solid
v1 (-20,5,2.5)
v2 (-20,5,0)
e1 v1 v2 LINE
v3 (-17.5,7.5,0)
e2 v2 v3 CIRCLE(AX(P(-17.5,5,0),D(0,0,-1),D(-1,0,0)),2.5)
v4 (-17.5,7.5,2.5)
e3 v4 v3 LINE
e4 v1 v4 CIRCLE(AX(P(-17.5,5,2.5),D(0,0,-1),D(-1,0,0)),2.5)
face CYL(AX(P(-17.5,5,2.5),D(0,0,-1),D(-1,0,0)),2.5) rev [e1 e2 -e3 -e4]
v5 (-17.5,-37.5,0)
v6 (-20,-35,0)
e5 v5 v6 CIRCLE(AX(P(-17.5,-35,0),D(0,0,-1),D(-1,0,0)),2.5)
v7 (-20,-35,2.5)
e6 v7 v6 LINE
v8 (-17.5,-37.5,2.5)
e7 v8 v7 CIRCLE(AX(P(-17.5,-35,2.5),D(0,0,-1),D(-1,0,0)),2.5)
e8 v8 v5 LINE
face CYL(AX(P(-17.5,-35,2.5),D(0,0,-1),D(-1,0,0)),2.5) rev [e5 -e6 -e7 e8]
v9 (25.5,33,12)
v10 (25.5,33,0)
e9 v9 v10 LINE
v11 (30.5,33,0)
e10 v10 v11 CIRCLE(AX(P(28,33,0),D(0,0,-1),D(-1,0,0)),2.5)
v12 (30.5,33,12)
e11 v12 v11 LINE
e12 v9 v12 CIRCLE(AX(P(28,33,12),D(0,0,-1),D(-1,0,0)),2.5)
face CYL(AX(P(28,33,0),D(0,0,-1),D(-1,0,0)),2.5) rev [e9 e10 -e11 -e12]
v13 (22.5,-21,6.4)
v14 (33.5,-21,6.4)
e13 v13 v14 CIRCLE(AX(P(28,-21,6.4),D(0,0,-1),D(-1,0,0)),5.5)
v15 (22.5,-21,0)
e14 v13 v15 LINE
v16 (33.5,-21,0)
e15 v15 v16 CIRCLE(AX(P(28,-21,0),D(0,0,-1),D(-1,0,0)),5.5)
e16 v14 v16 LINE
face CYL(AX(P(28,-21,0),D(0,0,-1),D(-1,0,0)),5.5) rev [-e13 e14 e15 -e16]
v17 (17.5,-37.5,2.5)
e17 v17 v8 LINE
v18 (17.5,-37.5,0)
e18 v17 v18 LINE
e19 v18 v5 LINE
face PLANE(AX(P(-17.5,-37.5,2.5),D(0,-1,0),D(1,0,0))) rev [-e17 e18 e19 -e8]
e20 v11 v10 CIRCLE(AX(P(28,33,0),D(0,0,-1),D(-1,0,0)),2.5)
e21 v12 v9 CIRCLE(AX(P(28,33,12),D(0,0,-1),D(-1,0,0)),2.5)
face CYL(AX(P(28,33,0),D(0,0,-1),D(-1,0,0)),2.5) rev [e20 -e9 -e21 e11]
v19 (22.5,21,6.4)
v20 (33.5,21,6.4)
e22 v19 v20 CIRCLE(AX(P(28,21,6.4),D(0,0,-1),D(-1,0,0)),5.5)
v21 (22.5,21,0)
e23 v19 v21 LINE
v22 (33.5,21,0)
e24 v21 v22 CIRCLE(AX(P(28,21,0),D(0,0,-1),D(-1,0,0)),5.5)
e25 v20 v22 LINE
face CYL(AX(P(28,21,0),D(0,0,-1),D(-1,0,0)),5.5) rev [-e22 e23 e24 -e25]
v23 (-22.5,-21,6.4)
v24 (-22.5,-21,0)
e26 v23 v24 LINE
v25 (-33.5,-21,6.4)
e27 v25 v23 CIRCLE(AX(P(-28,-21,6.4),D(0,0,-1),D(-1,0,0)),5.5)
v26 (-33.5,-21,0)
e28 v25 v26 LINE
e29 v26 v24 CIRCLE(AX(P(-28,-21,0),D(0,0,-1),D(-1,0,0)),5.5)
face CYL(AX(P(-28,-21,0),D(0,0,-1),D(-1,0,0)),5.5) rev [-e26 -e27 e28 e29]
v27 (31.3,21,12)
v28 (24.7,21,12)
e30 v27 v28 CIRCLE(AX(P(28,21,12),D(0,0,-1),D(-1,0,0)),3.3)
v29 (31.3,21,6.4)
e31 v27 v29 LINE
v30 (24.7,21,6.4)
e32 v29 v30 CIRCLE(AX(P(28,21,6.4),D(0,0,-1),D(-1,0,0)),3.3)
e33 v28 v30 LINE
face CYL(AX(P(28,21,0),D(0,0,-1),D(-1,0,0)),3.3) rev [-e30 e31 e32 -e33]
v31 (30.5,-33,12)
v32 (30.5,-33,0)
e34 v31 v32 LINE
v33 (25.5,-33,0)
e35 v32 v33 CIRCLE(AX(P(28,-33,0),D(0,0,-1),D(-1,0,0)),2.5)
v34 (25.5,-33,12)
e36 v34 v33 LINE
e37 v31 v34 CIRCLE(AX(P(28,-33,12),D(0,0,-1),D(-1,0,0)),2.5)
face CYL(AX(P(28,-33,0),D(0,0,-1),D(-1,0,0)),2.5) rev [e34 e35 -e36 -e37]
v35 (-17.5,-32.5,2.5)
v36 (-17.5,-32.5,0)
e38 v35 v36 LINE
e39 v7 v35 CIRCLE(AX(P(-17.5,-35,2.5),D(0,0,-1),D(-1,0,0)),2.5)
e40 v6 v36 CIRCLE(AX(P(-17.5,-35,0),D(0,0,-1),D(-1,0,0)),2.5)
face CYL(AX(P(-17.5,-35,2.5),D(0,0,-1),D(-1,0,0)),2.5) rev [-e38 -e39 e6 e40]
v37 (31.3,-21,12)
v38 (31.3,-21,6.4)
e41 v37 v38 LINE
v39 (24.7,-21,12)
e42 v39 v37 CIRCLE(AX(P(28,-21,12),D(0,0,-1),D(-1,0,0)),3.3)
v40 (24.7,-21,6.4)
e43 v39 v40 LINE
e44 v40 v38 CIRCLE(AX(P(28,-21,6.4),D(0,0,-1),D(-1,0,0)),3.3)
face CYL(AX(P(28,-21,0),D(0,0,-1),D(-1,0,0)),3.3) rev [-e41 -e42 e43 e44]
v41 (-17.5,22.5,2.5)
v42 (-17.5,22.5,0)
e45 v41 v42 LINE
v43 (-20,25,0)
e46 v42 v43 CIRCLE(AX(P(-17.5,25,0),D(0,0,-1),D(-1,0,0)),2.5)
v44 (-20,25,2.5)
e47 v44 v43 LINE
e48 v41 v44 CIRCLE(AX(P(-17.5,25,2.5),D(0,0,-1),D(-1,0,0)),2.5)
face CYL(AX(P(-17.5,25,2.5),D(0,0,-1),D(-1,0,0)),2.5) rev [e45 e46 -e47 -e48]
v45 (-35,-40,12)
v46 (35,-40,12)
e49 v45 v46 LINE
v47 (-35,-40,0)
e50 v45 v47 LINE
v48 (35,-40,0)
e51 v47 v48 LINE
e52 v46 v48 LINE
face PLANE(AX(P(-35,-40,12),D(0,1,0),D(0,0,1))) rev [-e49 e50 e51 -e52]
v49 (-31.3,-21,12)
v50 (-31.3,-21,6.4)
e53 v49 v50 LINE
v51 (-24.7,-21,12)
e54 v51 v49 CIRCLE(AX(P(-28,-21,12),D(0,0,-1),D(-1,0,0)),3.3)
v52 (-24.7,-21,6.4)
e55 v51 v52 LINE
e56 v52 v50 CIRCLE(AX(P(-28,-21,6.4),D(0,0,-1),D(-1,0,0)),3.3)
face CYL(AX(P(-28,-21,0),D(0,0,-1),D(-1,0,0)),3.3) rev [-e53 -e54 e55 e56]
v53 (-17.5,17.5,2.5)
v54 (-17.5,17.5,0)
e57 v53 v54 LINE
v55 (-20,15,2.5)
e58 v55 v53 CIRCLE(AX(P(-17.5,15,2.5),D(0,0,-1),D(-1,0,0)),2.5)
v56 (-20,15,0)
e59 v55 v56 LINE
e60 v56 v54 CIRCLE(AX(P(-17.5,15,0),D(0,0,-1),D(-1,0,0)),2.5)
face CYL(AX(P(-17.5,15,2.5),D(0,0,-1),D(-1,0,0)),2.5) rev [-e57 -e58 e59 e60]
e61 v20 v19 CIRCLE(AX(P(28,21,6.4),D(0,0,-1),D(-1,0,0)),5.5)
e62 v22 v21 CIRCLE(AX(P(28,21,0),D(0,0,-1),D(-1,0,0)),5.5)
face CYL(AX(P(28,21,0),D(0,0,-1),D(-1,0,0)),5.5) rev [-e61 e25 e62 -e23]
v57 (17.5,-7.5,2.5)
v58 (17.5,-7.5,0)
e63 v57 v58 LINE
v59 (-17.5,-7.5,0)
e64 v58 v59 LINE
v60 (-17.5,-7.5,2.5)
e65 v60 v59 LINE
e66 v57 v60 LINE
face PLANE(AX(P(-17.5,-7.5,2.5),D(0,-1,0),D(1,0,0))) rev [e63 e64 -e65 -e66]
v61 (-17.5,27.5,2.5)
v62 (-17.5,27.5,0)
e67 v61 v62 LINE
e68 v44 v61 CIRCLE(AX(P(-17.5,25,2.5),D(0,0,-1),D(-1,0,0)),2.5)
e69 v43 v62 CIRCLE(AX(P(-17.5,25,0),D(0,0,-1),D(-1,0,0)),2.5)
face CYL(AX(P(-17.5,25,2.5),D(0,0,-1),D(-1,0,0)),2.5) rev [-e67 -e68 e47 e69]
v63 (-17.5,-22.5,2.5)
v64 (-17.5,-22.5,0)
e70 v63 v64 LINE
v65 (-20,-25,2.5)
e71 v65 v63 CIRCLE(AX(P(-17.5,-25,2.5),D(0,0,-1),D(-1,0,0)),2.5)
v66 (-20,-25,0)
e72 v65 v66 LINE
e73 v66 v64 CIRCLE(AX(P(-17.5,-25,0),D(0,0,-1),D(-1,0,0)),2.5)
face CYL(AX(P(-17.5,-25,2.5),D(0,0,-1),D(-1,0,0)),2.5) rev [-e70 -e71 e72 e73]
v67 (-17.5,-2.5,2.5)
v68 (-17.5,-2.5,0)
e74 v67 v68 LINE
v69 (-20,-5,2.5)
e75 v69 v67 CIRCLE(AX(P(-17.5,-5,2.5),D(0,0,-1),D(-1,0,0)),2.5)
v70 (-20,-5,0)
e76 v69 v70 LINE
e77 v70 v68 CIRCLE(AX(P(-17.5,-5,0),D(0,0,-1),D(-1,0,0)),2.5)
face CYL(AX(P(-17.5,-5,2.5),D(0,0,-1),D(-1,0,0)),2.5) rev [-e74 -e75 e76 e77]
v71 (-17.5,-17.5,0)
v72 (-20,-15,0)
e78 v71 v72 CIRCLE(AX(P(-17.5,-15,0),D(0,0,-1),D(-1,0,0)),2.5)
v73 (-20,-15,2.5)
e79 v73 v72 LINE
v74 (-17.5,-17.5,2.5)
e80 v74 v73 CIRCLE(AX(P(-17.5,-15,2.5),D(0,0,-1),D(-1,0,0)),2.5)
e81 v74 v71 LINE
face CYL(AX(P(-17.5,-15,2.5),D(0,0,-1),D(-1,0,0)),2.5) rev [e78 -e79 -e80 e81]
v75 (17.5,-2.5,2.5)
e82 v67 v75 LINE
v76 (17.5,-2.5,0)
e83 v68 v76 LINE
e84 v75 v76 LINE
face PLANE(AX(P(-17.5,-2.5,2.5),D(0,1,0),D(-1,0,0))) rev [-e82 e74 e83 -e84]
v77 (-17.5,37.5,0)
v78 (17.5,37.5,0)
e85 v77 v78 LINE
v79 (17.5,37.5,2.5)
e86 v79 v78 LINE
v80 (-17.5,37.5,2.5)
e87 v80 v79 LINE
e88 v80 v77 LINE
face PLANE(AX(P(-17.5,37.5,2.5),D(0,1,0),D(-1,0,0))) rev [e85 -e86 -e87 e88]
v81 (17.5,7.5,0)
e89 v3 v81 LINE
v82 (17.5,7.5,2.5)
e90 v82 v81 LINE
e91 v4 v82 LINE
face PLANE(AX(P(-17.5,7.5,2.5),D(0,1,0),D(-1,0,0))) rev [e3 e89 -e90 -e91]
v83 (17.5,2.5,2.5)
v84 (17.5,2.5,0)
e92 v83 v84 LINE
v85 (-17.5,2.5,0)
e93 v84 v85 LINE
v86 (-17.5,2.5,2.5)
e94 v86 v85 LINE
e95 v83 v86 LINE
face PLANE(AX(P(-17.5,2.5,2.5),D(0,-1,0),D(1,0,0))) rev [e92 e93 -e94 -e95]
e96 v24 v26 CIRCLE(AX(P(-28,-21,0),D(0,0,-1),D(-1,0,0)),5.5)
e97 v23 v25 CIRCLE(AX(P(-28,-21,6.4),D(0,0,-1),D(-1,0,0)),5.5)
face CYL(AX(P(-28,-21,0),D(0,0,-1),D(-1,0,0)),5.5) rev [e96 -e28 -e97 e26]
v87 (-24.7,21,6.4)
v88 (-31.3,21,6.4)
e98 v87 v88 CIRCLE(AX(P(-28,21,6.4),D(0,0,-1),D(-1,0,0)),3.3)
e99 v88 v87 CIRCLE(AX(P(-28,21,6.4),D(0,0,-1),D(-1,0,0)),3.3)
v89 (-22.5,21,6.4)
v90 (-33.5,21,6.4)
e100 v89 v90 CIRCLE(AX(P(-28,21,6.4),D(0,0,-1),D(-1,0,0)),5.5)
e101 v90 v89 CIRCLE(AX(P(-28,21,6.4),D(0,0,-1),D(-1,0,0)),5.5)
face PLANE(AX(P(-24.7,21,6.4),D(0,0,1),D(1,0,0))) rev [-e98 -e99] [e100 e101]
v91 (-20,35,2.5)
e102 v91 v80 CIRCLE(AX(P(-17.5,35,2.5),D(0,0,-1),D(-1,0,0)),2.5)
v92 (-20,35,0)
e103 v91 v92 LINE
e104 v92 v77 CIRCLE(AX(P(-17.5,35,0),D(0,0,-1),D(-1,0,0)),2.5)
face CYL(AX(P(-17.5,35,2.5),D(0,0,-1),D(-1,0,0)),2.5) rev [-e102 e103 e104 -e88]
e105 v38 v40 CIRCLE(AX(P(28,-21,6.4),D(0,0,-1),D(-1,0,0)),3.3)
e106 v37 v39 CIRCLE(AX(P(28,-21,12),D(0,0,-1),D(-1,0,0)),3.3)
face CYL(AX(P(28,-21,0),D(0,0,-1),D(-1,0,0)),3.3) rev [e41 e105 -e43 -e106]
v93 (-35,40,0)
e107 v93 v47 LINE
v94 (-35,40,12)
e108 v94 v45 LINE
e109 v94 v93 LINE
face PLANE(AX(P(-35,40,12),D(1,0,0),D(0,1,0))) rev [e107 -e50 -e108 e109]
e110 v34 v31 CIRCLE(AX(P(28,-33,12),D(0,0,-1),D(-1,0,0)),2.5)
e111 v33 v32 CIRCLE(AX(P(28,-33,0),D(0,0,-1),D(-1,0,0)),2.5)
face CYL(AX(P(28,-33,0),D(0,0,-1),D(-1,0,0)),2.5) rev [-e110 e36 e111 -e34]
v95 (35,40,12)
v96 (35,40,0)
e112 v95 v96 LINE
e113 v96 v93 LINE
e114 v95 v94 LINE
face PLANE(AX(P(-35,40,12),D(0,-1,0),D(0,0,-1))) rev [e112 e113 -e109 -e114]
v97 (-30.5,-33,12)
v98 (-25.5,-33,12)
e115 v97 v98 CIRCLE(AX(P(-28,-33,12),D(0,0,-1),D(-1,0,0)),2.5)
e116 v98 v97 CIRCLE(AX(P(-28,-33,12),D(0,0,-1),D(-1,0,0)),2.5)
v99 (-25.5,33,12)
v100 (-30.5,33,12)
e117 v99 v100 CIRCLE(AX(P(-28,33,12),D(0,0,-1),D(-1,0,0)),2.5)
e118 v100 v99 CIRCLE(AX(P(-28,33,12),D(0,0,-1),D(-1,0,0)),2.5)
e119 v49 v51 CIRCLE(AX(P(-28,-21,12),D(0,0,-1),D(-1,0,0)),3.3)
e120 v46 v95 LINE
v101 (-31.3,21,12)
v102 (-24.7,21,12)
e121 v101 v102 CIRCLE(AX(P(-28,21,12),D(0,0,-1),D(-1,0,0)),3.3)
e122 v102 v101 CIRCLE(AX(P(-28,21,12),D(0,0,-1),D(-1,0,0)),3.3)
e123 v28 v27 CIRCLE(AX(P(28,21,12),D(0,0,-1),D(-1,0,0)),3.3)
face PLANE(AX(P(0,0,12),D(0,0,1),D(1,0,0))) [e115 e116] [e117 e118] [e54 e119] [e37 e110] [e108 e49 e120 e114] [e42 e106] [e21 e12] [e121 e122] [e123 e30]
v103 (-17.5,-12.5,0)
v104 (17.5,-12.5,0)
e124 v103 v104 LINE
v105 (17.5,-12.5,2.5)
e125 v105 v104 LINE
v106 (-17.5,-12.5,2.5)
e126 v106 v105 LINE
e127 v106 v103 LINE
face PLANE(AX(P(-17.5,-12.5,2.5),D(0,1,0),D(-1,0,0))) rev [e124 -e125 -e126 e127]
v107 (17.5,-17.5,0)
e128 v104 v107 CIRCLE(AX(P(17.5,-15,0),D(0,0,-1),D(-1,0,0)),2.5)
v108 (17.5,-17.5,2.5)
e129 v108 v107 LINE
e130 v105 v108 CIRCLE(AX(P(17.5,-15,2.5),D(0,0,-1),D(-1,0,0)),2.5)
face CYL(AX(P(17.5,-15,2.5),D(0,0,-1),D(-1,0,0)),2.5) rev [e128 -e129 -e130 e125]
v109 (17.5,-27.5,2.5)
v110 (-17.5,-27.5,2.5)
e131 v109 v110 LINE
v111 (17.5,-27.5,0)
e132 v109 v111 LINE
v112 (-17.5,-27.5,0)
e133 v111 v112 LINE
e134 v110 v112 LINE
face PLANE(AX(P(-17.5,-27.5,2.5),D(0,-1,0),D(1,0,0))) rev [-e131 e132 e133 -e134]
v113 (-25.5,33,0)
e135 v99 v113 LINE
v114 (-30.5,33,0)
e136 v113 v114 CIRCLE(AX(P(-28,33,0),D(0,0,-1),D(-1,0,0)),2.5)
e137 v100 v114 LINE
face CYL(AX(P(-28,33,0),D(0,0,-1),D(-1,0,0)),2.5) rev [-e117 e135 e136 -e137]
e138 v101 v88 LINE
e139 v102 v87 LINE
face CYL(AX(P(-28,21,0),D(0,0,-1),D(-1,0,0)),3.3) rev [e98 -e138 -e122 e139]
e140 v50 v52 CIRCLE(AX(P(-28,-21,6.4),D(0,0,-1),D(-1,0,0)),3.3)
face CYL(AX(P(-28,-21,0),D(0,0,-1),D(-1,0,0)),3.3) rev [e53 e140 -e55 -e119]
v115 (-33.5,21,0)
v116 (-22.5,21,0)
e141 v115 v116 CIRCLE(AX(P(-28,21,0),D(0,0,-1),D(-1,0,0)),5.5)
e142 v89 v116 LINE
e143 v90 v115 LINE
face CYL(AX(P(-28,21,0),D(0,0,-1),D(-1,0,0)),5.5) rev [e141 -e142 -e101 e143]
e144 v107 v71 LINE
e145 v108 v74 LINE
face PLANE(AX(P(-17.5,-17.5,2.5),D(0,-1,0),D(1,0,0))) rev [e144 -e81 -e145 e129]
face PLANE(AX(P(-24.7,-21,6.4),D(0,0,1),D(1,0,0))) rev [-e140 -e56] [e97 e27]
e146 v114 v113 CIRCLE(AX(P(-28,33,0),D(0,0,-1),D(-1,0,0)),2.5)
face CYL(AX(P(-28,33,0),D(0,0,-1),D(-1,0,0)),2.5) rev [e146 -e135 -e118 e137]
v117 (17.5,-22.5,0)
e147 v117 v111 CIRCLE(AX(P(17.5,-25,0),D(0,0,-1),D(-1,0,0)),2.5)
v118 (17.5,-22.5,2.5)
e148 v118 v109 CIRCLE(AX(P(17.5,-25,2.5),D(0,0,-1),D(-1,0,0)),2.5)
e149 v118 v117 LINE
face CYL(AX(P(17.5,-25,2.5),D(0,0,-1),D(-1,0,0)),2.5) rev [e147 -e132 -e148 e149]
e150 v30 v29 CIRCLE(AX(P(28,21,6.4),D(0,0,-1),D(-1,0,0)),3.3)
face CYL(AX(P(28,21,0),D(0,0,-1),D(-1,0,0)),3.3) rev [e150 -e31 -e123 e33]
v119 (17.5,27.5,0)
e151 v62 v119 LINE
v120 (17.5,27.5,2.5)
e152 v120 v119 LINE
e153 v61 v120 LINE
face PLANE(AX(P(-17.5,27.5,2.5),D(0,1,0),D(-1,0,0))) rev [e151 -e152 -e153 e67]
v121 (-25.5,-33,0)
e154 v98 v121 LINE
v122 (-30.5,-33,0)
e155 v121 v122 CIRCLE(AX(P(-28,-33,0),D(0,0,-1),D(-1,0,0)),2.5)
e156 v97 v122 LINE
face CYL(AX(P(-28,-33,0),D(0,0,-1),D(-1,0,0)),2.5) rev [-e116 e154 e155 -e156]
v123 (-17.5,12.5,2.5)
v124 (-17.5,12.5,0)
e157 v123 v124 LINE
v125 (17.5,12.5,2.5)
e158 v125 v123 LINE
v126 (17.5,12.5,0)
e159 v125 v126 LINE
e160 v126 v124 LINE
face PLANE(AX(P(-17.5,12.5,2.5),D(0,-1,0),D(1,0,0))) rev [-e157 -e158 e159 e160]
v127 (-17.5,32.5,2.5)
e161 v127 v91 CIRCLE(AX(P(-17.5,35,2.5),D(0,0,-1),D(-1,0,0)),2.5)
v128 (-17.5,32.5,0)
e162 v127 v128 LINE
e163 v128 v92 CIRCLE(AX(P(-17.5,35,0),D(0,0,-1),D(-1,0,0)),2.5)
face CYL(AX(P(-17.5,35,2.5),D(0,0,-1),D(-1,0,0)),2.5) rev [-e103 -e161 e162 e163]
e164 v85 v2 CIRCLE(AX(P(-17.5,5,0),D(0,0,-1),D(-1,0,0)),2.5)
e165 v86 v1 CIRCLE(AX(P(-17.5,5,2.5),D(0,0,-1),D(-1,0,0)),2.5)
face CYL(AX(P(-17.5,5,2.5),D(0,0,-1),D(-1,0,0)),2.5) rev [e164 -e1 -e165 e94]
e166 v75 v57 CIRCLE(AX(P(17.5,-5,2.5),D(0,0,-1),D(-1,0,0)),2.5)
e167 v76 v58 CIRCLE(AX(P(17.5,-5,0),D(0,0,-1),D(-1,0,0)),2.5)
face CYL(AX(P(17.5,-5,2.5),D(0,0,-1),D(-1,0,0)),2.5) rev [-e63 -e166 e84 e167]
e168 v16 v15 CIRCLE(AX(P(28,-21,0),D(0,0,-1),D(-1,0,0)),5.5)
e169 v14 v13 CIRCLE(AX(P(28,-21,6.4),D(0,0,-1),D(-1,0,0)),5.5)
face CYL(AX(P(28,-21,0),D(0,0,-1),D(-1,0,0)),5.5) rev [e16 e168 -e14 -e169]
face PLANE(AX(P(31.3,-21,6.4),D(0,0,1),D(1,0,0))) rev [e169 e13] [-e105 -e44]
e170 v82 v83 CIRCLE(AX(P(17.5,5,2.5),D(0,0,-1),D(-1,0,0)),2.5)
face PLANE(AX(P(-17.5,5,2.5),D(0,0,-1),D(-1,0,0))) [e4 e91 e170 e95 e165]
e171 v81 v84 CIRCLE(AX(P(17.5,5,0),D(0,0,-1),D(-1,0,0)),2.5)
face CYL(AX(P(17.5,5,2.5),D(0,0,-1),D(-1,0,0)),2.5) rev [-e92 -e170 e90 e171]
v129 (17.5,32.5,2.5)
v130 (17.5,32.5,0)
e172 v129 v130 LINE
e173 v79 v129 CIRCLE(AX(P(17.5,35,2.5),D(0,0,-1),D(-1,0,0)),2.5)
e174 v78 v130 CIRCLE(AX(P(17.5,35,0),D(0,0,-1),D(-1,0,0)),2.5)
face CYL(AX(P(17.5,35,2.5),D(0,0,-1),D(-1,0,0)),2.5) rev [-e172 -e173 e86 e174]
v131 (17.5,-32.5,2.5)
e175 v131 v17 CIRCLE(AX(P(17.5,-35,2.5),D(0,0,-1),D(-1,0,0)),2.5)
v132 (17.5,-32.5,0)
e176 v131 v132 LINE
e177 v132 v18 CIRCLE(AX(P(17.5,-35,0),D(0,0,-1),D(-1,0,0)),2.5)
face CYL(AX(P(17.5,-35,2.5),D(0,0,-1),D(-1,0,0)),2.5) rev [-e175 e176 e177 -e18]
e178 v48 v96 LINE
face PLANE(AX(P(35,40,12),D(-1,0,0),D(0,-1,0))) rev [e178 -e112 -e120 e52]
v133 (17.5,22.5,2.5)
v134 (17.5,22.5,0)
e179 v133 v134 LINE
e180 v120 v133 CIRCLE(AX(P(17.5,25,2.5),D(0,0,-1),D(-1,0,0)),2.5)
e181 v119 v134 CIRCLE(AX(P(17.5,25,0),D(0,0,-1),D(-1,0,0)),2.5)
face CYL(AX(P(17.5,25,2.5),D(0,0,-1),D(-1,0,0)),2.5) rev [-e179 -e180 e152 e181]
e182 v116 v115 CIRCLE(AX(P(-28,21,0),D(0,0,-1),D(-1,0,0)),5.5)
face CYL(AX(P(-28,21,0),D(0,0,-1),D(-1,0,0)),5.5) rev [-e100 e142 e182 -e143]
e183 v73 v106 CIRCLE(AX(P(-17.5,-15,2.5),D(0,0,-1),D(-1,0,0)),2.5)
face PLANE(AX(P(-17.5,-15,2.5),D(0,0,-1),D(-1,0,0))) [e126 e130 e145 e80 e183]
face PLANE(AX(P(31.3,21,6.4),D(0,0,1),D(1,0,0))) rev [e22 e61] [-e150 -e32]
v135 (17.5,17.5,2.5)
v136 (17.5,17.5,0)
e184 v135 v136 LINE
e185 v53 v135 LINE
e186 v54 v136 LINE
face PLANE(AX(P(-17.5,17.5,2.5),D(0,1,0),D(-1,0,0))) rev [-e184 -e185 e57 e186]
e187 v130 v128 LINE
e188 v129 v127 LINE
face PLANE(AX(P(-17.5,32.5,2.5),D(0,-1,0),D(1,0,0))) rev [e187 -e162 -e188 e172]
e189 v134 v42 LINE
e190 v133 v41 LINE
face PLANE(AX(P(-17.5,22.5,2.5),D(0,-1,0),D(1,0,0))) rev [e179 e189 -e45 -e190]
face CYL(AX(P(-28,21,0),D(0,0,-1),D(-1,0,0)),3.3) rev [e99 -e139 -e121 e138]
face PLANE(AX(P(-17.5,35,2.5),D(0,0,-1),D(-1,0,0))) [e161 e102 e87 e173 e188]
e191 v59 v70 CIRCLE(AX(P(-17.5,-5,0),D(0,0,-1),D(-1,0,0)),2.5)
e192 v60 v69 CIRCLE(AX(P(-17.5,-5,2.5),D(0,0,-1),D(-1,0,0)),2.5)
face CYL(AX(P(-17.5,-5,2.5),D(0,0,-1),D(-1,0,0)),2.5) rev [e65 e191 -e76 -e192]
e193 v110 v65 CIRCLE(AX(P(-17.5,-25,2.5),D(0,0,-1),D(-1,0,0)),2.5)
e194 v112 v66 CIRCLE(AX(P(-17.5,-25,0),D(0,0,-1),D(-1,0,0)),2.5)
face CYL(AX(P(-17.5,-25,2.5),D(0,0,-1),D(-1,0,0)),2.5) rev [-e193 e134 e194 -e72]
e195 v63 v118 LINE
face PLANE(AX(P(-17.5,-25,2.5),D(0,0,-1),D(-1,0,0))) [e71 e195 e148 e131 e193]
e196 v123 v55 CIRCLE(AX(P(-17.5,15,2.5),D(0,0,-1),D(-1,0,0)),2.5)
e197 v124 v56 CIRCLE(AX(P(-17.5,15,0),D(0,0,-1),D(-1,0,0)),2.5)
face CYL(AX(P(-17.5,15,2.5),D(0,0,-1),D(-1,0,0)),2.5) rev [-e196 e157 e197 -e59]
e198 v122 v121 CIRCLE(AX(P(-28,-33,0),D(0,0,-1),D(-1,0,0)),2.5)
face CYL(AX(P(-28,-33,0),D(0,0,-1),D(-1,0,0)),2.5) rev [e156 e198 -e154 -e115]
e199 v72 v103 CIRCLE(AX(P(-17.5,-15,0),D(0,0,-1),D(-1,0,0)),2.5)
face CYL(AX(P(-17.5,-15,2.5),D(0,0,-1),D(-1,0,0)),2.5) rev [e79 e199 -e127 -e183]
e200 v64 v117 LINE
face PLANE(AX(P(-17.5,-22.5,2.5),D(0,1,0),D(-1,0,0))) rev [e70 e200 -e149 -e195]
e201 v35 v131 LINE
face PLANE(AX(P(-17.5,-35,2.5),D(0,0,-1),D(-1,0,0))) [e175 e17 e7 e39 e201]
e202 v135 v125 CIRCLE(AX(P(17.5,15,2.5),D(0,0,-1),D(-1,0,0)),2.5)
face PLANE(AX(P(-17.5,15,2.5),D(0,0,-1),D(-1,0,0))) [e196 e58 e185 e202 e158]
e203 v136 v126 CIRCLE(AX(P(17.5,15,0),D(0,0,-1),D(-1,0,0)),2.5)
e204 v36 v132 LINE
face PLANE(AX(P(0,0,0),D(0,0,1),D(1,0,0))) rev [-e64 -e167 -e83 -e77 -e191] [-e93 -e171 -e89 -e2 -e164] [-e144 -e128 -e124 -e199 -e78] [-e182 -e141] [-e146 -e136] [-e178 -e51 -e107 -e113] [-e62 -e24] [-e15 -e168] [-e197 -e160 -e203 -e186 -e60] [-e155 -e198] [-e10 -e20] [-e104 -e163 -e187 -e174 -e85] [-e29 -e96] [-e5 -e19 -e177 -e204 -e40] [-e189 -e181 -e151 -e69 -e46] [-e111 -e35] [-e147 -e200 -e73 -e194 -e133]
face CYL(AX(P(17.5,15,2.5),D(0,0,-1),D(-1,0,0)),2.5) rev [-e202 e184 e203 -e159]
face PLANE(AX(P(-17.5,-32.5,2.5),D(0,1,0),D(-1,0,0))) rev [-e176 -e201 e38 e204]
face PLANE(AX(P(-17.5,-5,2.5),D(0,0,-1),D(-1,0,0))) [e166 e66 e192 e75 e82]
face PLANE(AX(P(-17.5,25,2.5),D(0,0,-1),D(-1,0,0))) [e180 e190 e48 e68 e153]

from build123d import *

# Parameters (mm, degrees)
SKETCH_1_W                     = 70
SKETCH_1_H                     = 80
EXTRUDE_1_DEPTH                = 12
HOLE_WIZARD_M6_1_D             = 5
HOLE_WIZARD_M6_1_2_D           = 6.6
HOLE_WIZARD_M6_1_2_CBORE_D     = 11
HOLE_WIZARD_M6_1_2_CBORE_DEPTH = 6.4
CUT_EXTRUDE_1_DEPTH            = 2.5
PATTERN_LINEAR_1_COUNT         = 8
PATTERN_LINEAR_1_PITCH         = 10


with BuildPart() as part:
    # 草图1 → 凸台-拉伸1 (new body)
    with BuildSketch(Plane.XY):
        Rectangle(SKETCH_1_W, SKETCH_1_H)
    extrude(amount=EXTRUDE_1_DEPTH)

    # Hole Wizard M6 _1 (through all)
    with Locations(Plane(origin=(0, 0, 0), x_dir=(-1, 0, 0), z_dir=(0, 0, -1))):
        with Locations((-28, -33), (-28, 33), (28, 33), (28, -33)):
            Hole(HOLE_WIZARD_M6_1_D / 2)

    # Hole Wizard M6 _1 2 (through all)
    with Locations(Plane(origin=(0, 0, 0), x_dir=(-1, 0, 0), z_dir=(0, 0, -1))):
        with Locations((-28, -21), (-28, 21), (28, -21), (28, 21)):
            CounterBoreHole(HOLE_WIZARD_M6_1_2_D / 2, HOLE_WIZARD_M6_1_2_CBORE_D / 2, HOLE_WIZARD_M6_1_2_CBORE_DEPTH)

    # 草图6 → 切除-拉伸1 (cut)
    with BuildSketch(Plane(origin=(0, 0, 0), x_dir=(-1, 0, 0), z_dir=(0, 0, -1))):
        with BuildLine():
            Line((17.5, 32.5), (-17.5, 32.5))
            ThreePointArc((-17.5, 32.5), (-20, 35), (-17.5, 37.5))
            Line((-17.5, 37.5), (17.5, 37.5))
            ThreePointArc((17.5, 37.5), (20, 35), (17.5, 32.5))
        make_face()
    cut_extrude_1 = extrude(amount=-CUT_EXTRUDE_1_DEPTH, mode=Mode.SUBTRACT)

    # 阵列(线性)1: 切除-拉伸1 ×8
    with Locations(*[(0, -i * PATTERN_LINEAR_1_PITCH, 0) for i in range(1, PATTERN_LINEAR_1_COUNT)]):
        add(cut_extrude_1, mode=Mode.SUBTRACT)


solid = part.part
